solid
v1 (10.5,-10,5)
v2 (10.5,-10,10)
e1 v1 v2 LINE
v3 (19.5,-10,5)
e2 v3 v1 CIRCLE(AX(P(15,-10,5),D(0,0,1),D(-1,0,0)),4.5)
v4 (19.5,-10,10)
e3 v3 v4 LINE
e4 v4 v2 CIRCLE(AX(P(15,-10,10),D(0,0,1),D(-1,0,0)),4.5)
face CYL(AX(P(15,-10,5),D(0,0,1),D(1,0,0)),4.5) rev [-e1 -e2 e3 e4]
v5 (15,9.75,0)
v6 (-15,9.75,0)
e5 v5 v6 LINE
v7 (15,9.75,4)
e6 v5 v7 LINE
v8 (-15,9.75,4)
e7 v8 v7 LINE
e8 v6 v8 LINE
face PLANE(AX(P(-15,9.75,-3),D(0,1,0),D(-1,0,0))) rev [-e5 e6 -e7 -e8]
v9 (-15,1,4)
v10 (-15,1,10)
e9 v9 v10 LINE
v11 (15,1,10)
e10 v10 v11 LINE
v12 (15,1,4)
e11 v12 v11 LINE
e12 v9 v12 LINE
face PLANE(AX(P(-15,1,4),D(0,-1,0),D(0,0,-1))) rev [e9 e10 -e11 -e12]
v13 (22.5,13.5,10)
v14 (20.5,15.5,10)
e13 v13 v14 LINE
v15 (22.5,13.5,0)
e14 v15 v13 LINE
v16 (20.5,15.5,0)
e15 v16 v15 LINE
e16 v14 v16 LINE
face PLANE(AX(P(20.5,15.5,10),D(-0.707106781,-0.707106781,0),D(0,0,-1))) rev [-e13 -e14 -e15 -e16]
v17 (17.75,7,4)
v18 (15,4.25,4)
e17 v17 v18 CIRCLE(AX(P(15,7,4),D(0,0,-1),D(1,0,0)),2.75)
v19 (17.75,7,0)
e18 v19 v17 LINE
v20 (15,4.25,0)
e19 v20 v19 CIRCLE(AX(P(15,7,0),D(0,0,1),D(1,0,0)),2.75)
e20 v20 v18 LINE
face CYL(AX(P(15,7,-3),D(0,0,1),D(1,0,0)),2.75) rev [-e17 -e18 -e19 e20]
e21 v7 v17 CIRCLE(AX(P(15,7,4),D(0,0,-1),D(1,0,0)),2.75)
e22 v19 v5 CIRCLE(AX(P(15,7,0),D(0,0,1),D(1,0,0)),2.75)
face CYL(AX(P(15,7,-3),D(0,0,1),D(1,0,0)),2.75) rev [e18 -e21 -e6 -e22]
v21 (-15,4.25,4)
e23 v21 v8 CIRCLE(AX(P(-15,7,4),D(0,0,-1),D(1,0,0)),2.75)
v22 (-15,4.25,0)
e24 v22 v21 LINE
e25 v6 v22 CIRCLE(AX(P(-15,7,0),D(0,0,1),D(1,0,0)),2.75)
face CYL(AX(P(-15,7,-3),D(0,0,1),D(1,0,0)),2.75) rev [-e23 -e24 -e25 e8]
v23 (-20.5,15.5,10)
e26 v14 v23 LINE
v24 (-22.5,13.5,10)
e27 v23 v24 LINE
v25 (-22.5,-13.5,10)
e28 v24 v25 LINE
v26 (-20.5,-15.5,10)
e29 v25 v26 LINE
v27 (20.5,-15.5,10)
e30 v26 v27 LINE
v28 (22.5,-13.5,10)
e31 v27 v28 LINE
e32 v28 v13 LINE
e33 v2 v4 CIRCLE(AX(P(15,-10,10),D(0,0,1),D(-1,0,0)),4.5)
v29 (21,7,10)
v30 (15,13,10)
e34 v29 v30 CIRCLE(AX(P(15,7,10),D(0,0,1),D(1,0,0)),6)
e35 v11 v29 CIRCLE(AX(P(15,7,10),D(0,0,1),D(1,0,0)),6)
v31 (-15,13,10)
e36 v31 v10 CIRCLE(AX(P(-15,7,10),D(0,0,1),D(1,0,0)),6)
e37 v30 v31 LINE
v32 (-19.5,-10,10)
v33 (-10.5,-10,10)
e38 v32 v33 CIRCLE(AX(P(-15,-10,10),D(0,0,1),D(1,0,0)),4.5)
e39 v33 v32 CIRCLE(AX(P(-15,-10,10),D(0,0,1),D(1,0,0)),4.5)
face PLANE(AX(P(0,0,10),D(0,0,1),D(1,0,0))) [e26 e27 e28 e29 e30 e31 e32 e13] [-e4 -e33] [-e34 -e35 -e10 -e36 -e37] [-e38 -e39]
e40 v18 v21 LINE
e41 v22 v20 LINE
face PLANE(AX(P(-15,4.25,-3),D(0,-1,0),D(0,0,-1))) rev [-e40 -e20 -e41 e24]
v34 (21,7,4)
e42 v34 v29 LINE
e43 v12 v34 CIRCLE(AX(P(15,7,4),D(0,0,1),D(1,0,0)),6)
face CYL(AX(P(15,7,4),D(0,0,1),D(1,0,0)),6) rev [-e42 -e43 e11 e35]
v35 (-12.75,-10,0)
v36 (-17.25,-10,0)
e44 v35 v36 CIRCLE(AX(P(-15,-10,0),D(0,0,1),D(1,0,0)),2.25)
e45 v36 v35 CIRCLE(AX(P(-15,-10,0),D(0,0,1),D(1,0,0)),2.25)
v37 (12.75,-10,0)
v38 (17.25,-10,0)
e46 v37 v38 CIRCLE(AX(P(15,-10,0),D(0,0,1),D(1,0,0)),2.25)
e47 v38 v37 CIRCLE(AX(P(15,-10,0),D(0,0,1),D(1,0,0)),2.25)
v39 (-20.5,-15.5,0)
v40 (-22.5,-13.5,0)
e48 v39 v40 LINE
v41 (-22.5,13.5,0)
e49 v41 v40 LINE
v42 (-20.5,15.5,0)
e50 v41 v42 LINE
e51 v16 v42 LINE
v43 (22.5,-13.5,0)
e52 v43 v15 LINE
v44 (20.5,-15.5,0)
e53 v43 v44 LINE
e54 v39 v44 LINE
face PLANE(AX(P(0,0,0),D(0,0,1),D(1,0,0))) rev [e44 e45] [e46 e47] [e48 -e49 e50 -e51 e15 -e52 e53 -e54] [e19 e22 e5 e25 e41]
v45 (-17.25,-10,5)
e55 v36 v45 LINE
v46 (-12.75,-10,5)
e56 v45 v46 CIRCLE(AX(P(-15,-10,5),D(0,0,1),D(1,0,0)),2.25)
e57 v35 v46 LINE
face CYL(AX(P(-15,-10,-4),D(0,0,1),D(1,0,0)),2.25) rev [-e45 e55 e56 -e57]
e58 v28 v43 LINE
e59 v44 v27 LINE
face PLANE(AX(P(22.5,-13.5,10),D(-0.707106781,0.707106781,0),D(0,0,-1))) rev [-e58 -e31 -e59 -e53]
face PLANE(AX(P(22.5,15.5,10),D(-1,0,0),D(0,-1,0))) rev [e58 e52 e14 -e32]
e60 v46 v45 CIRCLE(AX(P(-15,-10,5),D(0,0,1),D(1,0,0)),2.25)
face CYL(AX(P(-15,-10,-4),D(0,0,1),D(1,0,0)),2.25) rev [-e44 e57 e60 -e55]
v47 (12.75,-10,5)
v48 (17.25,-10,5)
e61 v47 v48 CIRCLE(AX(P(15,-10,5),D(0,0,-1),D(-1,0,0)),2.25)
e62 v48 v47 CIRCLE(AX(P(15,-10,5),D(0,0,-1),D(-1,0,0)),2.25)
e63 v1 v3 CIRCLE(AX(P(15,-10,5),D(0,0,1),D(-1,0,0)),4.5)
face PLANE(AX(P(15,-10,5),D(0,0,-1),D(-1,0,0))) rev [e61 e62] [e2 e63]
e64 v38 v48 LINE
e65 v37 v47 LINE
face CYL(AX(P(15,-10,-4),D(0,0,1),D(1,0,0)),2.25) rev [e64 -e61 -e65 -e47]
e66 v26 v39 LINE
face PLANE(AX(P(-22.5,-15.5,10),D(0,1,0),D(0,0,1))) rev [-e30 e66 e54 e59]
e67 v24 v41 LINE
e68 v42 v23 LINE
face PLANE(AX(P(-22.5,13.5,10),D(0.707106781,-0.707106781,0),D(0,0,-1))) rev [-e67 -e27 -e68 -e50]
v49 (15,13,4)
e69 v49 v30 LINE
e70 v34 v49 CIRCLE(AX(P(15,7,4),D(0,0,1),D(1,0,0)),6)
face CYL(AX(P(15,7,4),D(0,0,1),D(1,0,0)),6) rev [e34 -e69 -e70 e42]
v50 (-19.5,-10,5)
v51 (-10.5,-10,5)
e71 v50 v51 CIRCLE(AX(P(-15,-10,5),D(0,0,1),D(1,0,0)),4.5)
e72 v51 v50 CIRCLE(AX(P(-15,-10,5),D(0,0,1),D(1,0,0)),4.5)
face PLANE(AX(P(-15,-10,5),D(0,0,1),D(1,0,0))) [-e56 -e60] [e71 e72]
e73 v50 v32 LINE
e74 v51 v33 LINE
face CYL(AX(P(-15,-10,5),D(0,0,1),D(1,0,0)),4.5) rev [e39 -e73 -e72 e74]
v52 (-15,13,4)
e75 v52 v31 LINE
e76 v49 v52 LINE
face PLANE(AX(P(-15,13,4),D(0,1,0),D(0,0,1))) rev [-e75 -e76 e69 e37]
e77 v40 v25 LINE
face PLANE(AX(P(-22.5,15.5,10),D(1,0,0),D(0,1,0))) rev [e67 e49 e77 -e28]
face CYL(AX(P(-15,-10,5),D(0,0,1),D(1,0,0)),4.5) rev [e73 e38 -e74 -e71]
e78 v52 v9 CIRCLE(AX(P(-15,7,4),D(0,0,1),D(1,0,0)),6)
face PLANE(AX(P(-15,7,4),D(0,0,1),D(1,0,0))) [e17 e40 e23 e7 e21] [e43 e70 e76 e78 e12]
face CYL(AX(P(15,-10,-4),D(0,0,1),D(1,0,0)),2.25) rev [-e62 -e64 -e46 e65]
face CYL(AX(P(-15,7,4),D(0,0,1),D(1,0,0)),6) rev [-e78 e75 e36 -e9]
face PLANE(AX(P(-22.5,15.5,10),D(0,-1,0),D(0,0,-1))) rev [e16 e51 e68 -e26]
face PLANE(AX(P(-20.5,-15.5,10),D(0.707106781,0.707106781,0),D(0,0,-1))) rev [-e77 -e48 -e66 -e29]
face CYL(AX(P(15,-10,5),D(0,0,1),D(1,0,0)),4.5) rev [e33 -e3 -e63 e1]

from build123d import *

# Parameters (mm, degrees)
SKETCH1_W           = 45
SKETCH1_H           = 31
BOSS_EXTRUDE1_DEPTH = 10
CUT_EXTRUDE1_DEPTH  = 13
SKETCH3_R           = 4.5
CUT_EXTRUDE2_DEPTH  = 5
SKETCH4_R           = 2.25
CUT_EXTRUDE3_DEPTH  = 14
CHAMFER1_SIZE       = 2
CUT_EXTRUDE4_DEPTH  = 6


with BuildPart() as part:
    # Sketch1 → Boss-Extrude1 (new body)
    with BuildSketch(Plane.XY):
        Rectangle(SKETCH1_W, SKETCH1_H)
    extrude(amount=BOSS_EXTRUDE1_DEPTH)

    # Sketch2 → Cut-Extrude1 (cut)
    with BuildSketch(Plane.XY.offset(10)):
        with BuildLine():
            Line((-15, 9.75), (15, 9.75))
            ThreePointArc((15, 9.75), (17.75, 7), (15, 4.25))
            Line((15, 4.25), (-15, 4.25))
            ThreePointArc((-15, 4.25), (-17.75, 7), (-15, 9.75))
        make_face()
    extrude(amount=-CUT_EXTRUDE1_DEPTH, mode=Mode.SUBTRACT)

    # Sketch3 → Cut-Extrude2 (cut)
    with BuildSketch(Plane.XY.offset(10)):
        with Locations((-15, -10)):
            Circle(SKETCH3_R)
        with Locations(Location((15, -10, 0), (0, 0, 180))):
            Circle(SKETCH3_R)
    extrude(amount=-CUT_EXTRUDE2_DEPTH, mode=Mode.SUBTRACT)

    # Sketch4 → Cut-Extrude3 (cut)
    with BuildSketch(Plane.XY.offset(10)):
        with Locations((-15, -10)):
            Circle(SKETCH4_R)
        with Locations((15, -10)):
            Circle(SKETCH4_R)
    extrude(amount=-CUT_EXTRUDE3_DEPTH, mode=Mode.SUBTRACT)

    # Chamfer1
    chamfer1_edges = [part.edges().sort_by_distance(p)[0] for p in [
        (22.5, -15.5, 5),
        (-22.5, -15.5, 5),
        (-22.5, 15.5, 5),
        (22.5, 15.5, 5),
    ]]
    chamfer(chamfer1_edges, length=CHAMFER1_SIZE)

    # Sketch5 → Cut-Extrude4 (cut)
    with BuildSketch(Plane.XY.offset(10)):
        with BuildLine():
            Line((-15, 13), (15, 13))
            ThreePointArc((15, 13), (21, 7), (15, 1))
            Line((15, 1), (-15, 1))
            ThreePointArc((-15, 1), (-21, 7), (-15, 13))
        make_face()
    extrude(amount=-CUT_EXTRUDE4_DEPTH, mode=Mode.SUBTRACT)


solid = part.part
